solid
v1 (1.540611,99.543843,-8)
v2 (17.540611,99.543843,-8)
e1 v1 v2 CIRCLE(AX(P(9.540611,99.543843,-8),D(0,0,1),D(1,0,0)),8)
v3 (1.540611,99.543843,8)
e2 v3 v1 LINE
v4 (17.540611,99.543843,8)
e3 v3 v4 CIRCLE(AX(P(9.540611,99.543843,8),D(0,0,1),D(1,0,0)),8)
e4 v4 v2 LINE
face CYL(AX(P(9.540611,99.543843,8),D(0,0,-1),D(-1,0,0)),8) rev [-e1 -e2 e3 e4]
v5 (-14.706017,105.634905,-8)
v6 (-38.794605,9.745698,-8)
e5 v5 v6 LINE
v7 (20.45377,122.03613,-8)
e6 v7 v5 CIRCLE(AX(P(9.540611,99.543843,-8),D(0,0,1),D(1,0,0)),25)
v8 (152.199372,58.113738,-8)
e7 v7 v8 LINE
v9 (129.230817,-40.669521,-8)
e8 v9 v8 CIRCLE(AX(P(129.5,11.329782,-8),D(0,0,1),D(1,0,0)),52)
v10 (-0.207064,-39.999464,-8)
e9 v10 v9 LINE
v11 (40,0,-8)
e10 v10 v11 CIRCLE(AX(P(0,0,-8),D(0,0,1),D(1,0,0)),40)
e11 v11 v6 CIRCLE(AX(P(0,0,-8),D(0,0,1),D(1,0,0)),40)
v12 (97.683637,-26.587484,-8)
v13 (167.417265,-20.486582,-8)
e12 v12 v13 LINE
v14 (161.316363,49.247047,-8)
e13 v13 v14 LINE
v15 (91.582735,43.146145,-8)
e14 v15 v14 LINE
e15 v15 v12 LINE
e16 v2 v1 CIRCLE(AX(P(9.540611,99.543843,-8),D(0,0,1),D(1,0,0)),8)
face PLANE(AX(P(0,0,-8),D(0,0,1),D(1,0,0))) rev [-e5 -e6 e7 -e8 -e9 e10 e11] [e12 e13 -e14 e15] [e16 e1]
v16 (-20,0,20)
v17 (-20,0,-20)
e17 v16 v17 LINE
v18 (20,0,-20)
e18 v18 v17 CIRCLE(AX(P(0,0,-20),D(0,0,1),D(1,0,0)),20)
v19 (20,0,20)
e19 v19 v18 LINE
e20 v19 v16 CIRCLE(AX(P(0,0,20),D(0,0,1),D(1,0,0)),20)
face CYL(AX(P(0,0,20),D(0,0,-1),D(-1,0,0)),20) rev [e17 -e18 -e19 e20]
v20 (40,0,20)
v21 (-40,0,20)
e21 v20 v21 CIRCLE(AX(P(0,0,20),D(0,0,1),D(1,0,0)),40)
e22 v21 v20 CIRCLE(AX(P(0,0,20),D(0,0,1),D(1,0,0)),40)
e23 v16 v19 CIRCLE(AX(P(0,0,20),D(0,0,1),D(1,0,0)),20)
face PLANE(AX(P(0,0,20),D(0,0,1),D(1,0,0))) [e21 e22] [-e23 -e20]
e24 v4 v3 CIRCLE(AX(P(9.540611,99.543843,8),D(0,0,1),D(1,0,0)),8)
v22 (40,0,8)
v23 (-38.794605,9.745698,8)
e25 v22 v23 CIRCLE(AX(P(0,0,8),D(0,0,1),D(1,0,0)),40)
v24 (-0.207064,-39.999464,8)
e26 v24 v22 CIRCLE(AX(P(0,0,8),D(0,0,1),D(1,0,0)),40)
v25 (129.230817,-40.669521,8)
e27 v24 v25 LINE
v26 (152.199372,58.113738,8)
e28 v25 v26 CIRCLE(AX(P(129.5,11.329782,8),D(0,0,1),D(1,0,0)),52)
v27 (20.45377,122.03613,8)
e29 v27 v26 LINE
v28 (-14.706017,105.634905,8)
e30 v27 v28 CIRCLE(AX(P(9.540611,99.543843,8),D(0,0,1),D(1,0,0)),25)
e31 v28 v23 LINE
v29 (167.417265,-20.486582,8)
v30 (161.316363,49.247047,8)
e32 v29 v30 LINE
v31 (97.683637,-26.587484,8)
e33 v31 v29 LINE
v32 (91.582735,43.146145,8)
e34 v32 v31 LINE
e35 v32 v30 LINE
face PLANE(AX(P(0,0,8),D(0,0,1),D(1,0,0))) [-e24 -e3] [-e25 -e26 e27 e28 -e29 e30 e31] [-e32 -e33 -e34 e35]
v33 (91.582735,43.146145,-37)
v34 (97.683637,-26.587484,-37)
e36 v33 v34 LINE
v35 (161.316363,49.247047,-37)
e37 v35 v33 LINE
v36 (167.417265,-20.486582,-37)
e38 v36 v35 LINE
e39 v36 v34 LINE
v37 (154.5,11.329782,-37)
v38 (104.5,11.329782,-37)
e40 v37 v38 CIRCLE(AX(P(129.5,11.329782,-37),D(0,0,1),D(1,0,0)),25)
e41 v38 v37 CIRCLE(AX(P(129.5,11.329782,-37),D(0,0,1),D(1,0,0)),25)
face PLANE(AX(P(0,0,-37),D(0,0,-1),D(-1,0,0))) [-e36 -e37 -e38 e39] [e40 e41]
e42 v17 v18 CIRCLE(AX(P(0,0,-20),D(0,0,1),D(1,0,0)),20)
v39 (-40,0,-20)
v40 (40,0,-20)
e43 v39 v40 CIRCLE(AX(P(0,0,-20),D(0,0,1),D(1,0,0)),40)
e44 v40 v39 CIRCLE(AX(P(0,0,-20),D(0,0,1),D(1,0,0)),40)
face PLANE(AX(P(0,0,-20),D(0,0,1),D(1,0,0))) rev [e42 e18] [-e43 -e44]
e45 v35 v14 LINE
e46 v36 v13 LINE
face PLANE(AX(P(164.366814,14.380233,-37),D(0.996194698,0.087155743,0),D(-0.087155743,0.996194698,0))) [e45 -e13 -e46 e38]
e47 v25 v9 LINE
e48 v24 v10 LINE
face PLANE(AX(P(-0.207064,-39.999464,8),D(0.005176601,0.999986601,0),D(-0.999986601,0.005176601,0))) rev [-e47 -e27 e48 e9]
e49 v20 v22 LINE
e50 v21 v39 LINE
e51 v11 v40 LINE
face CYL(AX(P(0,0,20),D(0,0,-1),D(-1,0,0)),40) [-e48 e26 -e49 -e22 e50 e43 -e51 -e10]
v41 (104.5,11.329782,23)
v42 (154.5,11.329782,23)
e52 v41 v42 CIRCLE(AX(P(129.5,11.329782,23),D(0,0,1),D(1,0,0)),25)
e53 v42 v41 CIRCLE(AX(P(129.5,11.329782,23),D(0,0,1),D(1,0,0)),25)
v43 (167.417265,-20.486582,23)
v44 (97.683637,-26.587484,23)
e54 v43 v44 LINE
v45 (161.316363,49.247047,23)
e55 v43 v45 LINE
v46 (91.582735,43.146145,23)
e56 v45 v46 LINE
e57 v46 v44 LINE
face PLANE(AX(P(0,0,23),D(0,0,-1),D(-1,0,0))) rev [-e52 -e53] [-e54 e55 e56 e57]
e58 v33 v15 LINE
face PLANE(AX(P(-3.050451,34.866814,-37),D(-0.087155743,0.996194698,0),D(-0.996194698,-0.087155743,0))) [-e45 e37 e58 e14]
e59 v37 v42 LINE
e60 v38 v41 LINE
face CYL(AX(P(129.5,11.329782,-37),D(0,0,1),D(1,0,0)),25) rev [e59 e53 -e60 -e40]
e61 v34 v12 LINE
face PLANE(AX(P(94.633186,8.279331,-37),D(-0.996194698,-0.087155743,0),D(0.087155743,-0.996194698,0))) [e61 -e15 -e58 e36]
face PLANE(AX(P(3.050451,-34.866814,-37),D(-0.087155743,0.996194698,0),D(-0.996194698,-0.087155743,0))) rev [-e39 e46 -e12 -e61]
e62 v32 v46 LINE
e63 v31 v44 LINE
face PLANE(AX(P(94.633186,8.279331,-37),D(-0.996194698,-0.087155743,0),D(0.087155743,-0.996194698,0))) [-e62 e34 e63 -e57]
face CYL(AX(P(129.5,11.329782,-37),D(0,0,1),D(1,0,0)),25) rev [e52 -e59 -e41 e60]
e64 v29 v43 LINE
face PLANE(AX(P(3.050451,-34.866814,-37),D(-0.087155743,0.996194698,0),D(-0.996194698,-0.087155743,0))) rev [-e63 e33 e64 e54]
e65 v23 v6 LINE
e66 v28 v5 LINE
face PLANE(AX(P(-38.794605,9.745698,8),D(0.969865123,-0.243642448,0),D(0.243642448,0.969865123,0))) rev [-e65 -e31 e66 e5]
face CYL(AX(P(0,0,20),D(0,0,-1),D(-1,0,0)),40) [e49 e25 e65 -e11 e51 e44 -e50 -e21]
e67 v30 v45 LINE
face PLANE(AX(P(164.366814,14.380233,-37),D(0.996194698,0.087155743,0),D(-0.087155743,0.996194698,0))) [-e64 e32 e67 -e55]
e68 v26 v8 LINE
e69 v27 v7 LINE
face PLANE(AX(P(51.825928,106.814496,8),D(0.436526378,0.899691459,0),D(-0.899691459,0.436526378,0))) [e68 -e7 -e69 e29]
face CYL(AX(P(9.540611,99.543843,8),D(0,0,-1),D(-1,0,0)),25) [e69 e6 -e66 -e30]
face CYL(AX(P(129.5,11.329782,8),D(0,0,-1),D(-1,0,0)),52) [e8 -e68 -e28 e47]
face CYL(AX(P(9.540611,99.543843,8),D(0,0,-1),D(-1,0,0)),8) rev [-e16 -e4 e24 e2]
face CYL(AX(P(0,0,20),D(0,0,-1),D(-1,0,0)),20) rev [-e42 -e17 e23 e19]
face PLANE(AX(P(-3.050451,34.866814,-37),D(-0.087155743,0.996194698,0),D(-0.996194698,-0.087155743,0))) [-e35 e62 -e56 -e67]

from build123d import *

# Parameters (mm, degrees)
BASE_BLOCK_SKETCH_R              = 40
BASE_BLOCK_SKETCH_R_2            = 20
BASE_BLOCK_40MM_DEPTH            = 20
BRACKET_PLATE_PROFILE_SKETCH_R   = 20
BRACKET_PLATE_PROFILE_SKETCH_R_2 = 8
BRACKET_PLATE_16MM_DEPTH         = 8
BORE_BOSSES_DEPTH                = 15
BORE_BOSSES_DEPTH_BACK           = 45
BORE_BOSSES_START                = 8
SKETCH2_3_R                      = 25


with BuildPart() as part:
    # Base Block Sketch → Base Block 40mm (new, symmetric)
    with BuildSketch(Plane.XY):
        Circle(BASE_BLOCK_SKETCH_R)
        Circle(BASE_BLOCK_SKETCH_R_2, mode=Mode.SUBTRACT)
    extrude(amount=BASE_BLOCK_40MM_DEPTH, both=True)

    # Bracket Plate Profile Sketch → Bracket Plate 16mm (add, symmetric)
    with BuildSketch(Plane.XY):
        with BuildLine():
            ThreePointArc((-38.79460493, 9.74569794), (-31.60581958, -24.516773211), (-0.207064055, -39.999464052))
            Line((-0.207064055, -39.999464052), (129.230816729, -40.669521341))
            ThreePointArc((129.230816729, -40.669521341), (180.148903337, -0.446830099), (152.19937164, 58.1137378))
            Line((152.19937164, 58.1137378), (20.453770296, 122.036129806))
            ThreePointArc((20.453770296, 122.036129806), (-1.027993314, 122.200069977), (-14.706017228, 105.634904541))
            Line((-14.706017228, 105.634904541), (-38.79460493, 9.74569794))
        make_face()
        Circle(BRACKET_PLATE_PROFILE_SKETCH_R, mode=Mode.SUBTRACT)
        Polygon((132.550450996, -23.537032507), (97.683636563, -26.587483503), (94.633185567, 8.27933093), (91.582734571, 43.146145364), (126.449549004, 46.19659636), (161.316363437, 49.247047356), (164.366814433, 14.380232923), (167.417265429, -20.48658151), align=None, mode=Mode.SUBTRACT)
        with Locations((9.540610853, 99.543843328)):
            Circle(BRACKET_PLATE_PROFILE_SKETCH_R_2, mode=Mode.SUBTRACT)
    extrude(amount=BRACKET_PLATE_16MM_DEPTH, both=True)

    # Sketch2_3 → Bore Bosses (add, two sides: drawn at the far end of the back side and taken through both)
    with BuildSketch(Plane.XY.offset(BORE_BOSSES_START - BORE_BOSSES_DEPTH_BACK)):
        Polygon((94.633185567, 8.27933093), (91.582734571, 43.146145364), (126.449549004, 46.19659636), (161.316363437, 49.247047356), (164.366814433, 14.380232923), (167.417265429, -20.48658151), (132.550450996, -23.537032507), (97.683636563, -26.587483503), align=None)
        with Locations((129.5, 11.329781927)):
            Circle(SKETCH2_3_R, mode=Mode.SUBTRACT)
    extrude(amount=BORE_BOSSES_DEPTH + BORE_BOSSES_DEPTH_BACK)


solid = part.part
